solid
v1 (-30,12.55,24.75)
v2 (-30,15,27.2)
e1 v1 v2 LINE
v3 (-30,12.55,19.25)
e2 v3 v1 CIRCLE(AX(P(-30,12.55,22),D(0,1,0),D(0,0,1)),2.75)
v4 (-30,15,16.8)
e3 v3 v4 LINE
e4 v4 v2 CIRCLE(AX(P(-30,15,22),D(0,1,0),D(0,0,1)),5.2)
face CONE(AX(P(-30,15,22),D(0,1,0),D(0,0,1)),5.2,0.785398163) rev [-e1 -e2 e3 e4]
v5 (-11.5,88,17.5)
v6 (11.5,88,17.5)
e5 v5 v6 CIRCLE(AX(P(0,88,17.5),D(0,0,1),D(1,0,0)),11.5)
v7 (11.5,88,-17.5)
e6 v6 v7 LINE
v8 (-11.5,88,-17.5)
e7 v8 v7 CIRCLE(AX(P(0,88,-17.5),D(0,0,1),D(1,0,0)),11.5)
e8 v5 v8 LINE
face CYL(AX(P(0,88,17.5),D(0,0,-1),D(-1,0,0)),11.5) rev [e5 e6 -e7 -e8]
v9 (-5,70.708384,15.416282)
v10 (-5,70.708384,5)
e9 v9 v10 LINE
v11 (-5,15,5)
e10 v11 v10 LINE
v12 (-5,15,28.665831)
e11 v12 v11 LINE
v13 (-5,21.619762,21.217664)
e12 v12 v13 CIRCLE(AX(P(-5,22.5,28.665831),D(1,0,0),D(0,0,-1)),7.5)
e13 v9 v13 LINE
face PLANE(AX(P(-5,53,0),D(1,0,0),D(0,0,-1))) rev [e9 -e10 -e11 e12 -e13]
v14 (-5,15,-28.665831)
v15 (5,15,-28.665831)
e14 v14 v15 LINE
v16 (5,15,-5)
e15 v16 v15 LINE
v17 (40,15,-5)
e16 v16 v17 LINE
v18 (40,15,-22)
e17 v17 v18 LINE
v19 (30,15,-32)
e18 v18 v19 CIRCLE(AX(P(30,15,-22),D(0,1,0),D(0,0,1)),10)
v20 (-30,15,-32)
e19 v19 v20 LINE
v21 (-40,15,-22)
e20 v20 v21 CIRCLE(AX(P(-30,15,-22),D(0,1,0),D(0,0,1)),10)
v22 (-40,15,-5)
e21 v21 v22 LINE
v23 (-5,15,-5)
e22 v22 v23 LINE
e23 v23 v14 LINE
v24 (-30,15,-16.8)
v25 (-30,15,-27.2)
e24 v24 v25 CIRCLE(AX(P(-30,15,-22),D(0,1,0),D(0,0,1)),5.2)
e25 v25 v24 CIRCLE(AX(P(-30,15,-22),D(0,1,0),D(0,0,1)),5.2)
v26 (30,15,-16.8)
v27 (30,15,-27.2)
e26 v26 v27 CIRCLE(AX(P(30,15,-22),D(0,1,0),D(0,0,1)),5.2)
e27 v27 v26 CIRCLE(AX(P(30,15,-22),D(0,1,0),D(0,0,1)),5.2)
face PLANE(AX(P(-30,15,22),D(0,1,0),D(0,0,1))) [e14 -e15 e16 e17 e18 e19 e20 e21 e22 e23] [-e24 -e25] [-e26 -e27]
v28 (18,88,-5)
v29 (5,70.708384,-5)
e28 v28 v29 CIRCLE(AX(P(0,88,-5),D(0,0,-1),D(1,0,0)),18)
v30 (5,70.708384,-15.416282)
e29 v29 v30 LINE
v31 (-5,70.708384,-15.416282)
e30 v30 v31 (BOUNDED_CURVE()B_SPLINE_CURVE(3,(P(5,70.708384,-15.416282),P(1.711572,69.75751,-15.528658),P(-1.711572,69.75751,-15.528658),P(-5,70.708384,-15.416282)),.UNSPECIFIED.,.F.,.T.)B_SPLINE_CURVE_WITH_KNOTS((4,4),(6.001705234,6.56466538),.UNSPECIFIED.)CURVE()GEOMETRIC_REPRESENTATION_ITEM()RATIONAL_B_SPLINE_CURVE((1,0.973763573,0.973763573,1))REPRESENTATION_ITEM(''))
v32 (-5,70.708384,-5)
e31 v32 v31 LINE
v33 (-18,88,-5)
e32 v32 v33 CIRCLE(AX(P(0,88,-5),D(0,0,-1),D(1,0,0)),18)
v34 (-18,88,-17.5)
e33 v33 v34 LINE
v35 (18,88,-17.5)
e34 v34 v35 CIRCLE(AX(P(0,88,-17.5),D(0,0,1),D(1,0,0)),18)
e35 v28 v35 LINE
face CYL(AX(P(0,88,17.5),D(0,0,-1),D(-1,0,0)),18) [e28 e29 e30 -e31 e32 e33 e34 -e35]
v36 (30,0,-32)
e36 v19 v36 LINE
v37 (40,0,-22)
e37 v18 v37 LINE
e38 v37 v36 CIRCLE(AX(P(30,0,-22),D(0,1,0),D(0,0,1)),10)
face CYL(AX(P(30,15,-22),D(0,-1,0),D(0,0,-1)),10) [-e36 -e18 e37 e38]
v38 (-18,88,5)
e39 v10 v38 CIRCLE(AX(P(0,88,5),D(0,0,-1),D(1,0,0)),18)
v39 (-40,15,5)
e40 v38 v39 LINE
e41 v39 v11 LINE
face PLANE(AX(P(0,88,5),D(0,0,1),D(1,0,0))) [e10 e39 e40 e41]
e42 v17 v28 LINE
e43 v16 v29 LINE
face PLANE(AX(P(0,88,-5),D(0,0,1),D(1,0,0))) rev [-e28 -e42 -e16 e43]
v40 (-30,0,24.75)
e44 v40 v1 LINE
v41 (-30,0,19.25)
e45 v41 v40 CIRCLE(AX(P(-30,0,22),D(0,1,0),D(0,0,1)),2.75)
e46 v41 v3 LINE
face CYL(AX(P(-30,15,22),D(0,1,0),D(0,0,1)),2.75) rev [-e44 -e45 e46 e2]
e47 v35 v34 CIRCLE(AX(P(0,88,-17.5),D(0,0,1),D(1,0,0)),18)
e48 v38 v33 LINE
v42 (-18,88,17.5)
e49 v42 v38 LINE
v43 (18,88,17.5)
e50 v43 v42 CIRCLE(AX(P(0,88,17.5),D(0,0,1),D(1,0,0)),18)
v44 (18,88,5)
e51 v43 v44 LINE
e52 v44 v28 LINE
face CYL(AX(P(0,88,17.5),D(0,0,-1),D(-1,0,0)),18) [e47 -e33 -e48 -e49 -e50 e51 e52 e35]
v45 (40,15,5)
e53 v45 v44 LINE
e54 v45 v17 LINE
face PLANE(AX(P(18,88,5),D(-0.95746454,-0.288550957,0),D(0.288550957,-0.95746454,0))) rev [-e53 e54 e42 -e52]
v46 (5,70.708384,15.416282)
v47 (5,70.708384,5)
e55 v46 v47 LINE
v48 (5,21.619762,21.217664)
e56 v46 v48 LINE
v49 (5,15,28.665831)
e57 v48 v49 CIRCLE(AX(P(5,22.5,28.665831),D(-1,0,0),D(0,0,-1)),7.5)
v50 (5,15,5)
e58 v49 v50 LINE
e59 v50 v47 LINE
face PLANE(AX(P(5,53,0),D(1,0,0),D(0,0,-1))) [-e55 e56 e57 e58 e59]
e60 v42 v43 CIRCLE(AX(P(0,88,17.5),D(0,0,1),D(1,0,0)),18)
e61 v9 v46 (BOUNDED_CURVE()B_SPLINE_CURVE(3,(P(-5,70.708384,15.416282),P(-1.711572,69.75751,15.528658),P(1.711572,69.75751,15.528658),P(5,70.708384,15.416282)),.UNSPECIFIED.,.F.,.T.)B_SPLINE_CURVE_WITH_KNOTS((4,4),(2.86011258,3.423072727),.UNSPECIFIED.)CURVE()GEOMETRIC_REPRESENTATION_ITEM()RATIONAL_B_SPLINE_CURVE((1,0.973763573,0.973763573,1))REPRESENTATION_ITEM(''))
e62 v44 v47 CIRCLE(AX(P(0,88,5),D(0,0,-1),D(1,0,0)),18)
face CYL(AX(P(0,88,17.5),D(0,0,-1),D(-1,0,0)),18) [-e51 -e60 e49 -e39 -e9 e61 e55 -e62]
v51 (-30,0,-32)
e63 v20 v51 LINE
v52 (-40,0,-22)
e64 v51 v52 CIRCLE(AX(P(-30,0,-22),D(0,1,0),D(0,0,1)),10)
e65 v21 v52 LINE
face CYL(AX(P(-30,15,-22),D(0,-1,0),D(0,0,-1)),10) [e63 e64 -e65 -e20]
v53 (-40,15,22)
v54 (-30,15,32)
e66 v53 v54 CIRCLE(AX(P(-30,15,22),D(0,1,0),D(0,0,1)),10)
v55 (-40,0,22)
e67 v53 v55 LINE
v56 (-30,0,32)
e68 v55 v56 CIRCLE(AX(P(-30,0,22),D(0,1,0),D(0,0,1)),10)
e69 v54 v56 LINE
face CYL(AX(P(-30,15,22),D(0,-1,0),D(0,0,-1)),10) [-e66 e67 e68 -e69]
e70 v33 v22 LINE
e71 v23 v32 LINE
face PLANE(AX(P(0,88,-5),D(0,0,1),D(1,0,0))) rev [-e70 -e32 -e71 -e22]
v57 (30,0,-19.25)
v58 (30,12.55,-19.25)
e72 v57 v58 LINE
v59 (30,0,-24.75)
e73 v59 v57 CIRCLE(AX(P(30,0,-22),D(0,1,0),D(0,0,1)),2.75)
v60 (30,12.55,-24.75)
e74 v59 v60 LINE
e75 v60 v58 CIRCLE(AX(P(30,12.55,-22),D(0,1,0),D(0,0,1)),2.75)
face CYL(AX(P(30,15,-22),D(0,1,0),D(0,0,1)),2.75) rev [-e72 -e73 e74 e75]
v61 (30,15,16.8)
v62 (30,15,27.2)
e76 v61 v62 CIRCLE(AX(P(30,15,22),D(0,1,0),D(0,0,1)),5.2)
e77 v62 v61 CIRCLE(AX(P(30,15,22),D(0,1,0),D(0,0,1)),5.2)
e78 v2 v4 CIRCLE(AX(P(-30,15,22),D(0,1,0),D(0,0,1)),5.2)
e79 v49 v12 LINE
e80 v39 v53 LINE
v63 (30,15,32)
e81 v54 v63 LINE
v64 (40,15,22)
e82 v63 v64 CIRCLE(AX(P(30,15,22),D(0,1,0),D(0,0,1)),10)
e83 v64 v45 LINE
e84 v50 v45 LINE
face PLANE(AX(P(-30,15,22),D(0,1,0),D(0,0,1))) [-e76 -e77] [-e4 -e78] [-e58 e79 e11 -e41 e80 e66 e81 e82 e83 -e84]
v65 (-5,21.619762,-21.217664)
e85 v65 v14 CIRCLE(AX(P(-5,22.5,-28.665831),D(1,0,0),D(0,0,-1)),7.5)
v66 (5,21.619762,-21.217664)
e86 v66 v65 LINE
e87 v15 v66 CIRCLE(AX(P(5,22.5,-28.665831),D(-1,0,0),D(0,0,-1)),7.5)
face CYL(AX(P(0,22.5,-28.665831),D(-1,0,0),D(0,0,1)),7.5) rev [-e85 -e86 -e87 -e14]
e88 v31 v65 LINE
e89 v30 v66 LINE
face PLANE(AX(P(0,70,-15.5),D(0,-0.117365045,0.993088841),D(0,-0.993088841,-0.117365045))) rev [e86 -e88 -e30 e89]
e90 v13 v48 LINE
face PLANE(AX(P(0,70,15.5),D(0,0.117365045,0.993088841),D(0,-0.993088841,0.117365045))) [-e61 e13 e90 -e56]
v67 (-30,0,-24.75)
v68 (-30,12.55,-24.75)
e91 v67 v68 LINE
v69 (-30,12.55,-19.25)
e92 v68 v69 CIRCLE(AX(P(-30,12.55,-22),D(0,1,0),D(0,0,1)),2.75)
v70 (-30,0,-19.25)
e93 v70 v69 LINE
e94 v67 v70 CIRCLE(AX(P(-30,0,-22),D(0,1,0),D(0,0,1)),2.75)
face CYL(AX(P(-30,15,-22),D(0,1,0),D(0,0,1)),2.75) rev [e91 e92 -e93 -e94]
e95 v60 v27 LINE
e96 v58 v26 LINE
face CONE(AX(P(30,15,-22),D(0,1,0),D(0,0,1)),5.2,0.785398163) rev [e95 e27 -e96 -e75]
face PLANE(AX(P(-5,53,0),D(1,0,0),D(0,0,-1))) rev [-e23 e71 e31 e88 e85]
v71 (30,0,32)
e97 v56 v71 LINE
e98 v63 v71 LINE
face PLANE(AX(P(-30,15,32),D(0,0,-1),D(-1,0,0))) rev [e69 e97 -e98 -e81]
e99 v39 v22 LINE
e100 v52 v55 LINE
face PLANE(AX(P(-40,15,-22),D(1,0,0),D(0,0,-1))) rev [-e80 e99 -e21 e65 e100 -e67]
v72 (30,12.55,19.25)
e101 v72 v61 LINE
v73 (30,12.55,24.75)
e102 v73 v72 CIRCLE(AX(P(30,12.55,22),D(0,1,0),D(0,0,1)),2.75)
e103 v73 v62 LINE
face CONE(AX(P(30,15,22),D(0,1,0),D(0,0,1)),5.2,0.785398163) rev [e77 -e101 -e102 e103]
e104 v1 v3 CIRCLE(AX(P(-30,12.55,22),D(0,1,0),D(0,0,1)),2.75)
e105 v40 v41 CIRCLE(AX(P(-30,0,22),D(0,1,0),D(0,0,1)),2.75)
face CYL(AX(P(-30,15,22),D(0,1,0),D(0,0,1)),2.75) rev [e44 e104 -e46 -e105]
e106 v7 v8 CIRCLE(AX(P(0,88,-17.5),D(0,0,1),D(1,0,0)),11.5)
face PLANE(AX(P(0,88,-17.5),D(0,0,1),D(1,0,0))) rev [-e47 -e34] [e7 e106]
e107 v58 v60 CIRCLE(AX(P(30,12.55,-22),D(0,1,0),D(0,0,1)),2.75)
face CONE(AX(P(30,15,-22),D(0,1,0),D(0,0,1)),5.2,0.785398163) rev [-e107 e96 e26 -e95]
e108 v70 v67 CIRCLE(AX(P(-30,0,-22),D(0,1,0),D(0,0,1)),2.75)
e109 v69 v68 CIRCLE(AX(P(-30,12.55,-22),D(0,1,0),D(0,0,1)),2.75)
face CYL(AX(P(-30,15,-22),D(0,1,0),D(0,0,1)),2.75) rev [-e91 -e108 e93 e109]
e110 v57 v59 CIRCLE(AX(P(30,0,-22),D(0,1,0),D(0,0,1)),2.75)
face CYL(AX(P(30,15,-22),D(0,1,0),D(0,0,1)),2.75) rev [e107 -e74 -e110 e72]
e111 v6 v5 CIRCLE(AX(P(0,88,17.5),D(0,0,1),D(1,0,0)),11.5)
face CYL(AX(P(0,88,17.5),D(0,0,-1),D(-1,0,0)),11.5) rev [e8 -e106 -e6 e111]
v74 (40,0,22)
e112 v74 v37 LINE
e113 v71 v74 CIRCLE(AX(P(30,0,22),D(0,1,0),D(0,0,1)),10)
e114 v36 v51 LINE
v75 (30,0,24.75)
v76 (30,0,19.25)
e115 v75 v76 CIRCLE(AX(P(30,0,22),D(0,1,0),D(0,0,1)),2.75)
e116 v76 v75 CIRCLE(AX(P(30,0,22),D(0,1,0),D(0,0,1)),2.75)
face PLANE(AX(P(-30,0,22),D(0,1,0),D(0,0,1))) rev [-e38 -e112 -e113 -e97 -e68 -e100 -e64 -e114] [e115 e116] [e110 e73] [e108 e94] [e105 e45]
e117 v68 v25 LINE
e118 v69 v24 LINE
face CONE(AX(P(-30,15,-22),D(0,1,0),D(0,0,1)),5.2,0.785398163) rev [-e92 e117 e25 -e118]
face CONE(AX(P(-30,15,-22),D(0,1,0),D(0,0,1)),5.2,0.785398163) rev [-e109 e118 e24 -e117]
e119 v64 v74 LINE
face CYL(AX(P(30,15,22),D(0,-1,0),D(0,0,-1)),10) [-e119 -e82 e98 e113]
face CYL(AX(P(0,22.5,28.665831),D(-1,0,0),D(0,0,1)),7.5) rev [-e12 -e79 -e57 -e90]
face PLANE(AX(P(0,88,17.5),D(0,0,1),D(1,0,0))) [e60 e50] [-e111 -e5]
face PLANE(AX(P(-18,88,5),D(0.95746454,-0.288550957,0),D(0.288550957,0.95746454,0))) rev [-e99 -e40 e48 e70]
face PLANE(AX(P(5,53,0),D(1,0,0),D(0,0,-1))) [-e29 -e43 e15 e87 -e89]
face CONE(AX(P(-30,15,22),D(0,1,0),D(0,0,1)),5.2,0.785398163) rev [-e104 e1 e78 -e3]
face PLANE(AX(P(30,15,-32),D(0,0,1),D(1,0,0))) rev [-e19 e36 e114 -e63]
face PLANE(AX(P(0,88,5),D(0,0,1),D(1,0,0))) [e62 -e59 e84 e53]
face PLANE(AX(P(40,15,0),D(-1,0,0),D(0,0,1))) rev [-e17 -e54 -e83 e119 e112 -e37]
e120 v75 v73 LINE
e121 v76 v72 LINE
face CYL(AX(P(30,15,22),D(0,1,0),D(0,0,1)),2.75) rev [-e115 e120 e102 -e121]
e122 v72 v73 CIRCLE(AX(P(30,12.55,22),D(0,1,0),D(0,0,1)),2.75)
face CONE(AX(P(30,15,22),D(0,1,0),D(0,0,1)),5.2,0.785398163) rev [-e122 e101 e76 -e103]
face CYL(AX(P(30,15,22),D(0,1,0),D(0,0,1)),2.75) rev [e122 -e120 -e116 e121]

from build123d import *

# Parameters (mm, degrees)
BASE_PLATE_DEPTH                        = 15
BEARING_BOSS_SKETCH_R                   = 18
BEARING_BOSS_SKETCH_R_2                 = 11.5
BEARING_BOSS_36_BORE_23_DEPTH           = 17.5
UPRIGHT_WEB_DEPTH                       = 5
MOUNTING_HOLES_M5_CSK_D                 = 5.5
MOUNTING_HOLES_M5_CSK_CSINK_D           = 10.4
MOUNTING_HOLES_M5_CSK_CSINK_ANGLE       = 90
SUPPORT_RIB_REACH                       = 119.729
SUPPORT_RIB_SKETCH_WALL_W               = 292.839761494
SUPPORT_RIB_SKETCH_WALL_H               = 10
RIB_FILLET_R7_5_R                       = 7.5
RIB_FILLET_R7_5_OF_SUPPORT_RIB_MIRROR_R = 7.5


with BuildPart() as part:
    # Base Plate Sketch → Base Plate (new body)
    with BuildSketch(Plane(origin=(0, 0, 0), x_dir=(1, 0, 0), z_dir=(0, 1, 0))):
        with BuildLine():
            Line((40, 0), (40, 22))
            ThreePointArc((40, 22), (37.071067812, 29.071067812), (30, 32))
            Line((30, 32), (-30, 32))
            ThreePointArc((-30, 32), (-37.071067812, 29.071067812), (-40, 22))
            Line((-40, 22), (-40, -22))
            ThreePointArc((-40, -22), (-37.071067812, -29.071067812), (-30, -32))
            Line((-30, -32), (30, -32))
            ThreePointArc((30, -32), (37.071067812, -29.071067812), (40, -22))
            Line((40, -22), (40, 0))
        make_face()
    extrude(amount=BASE_PLATE_DEPTH)



with BuildPart() as body_2:
    # Bearing Boss Sketch → Bearing Boss Ø36 Bore Ø23 (new, symmetric)
    with BuildSketch(Plane.XY):
        with Locations((0, 88)):
            Circle(BEARING_BOSS_SKETCH_R)
        with Locations((0, 88)):
            Circle(BEARING_BOSS_SKETCH_R_2, mode=Mode.SUBTRACT)
    extrude(amount=BEARING_BOSS_36_BORE_23_DEPTH, both=True)


with BuildPart() as part_1:
    add(part.part)

    add(body_2.part)  # Upright Web merges body 2
    # Upright Web Sketch → Upright Web (add, symmetric)
    with BuildSketch(Plane.XY):
        with BuildLine():
            Line((18, 88), (40, 15))
            Line((40, 15), (-40, 15))
            Line((-40, 15), (-18, 88))
            ThreePointArc((-18, 88), (0, 70), (18, 88))
        make_face()
    extrude(amount=UPRIGHT_WEB_DEPTH, both=True)

    # Mounting Holes M5 CSK (through all)
    with Locations(Plane(origin=(0, 15, 0), x_dir=(1, 0, 0), z_dir=(0, 1, 0))):
        with Locations((-30, 22), (30, 22), (30, -22), (-30, -22)):
            CounterSinkHole(MOUNTING_HOLES_M5_CSK_D / 2, MOUNTING_HOLES_M5_CSK_CSINK_D / 2, counter_sink_angle=MOUNTING_HOLES_M5_CSK_CSINK_ANGLE)

    # Support Rib Sketch wall → Support Rib (add, up to next)
    with BuildSketch(Plane(origin=(0, 42.5, -18.75), x_dir=(0, -0.993088841064, -0.117365044853), z_dir=(0, 0.117365044853, -0.993088841064)), mode=Mode.PRIVATE) as support_rib_sk1:
        Rectangle(SUPPORT_RIB_SKETCH_WALL_W, SUPPORT_RIB_SKETCH_WALL_H)
    support_rib_tool1 = extrude(support_rib_sk1.sketch, amount=-SUPPORT_RIB_REACH, mode=Mode.PRIVATE) - part_1.part
    support_rib = support_rib_tool1.solids().sort_by_distance((0, 42.5, -18.75))[0]
    add(support_rib)

    # Rib Fillet R7.5
    rib_fillet_r7_5_edges = [part_1.edges().sort_by_distance(p)[0] for p in [
        (0, 15, -22),
    ]]
    fillet(rib_fillet_r7_5_edges, radius=RIB_FILLET_R7_5_R)

    # Support Rib Mirror: Support Rib across plane
    add(support_rib.mirror(Plane.XY))

    # Rib Fillet R7.5 of Support Rib Mirror
    rib_fillet_r7_5_of_support_rib_mirror_edges = [part_1.edges().sort_by_distance(p)[0] for p in [
        (0, 15, 22),
    ]]
    fillet(rib_fillet_r7_5_of_support_rib_mirror_edges, radius=RIB_FILLET_R7_5_OF_SUPPORT_RIB_MIRROR_R)


solid = part_1.part
